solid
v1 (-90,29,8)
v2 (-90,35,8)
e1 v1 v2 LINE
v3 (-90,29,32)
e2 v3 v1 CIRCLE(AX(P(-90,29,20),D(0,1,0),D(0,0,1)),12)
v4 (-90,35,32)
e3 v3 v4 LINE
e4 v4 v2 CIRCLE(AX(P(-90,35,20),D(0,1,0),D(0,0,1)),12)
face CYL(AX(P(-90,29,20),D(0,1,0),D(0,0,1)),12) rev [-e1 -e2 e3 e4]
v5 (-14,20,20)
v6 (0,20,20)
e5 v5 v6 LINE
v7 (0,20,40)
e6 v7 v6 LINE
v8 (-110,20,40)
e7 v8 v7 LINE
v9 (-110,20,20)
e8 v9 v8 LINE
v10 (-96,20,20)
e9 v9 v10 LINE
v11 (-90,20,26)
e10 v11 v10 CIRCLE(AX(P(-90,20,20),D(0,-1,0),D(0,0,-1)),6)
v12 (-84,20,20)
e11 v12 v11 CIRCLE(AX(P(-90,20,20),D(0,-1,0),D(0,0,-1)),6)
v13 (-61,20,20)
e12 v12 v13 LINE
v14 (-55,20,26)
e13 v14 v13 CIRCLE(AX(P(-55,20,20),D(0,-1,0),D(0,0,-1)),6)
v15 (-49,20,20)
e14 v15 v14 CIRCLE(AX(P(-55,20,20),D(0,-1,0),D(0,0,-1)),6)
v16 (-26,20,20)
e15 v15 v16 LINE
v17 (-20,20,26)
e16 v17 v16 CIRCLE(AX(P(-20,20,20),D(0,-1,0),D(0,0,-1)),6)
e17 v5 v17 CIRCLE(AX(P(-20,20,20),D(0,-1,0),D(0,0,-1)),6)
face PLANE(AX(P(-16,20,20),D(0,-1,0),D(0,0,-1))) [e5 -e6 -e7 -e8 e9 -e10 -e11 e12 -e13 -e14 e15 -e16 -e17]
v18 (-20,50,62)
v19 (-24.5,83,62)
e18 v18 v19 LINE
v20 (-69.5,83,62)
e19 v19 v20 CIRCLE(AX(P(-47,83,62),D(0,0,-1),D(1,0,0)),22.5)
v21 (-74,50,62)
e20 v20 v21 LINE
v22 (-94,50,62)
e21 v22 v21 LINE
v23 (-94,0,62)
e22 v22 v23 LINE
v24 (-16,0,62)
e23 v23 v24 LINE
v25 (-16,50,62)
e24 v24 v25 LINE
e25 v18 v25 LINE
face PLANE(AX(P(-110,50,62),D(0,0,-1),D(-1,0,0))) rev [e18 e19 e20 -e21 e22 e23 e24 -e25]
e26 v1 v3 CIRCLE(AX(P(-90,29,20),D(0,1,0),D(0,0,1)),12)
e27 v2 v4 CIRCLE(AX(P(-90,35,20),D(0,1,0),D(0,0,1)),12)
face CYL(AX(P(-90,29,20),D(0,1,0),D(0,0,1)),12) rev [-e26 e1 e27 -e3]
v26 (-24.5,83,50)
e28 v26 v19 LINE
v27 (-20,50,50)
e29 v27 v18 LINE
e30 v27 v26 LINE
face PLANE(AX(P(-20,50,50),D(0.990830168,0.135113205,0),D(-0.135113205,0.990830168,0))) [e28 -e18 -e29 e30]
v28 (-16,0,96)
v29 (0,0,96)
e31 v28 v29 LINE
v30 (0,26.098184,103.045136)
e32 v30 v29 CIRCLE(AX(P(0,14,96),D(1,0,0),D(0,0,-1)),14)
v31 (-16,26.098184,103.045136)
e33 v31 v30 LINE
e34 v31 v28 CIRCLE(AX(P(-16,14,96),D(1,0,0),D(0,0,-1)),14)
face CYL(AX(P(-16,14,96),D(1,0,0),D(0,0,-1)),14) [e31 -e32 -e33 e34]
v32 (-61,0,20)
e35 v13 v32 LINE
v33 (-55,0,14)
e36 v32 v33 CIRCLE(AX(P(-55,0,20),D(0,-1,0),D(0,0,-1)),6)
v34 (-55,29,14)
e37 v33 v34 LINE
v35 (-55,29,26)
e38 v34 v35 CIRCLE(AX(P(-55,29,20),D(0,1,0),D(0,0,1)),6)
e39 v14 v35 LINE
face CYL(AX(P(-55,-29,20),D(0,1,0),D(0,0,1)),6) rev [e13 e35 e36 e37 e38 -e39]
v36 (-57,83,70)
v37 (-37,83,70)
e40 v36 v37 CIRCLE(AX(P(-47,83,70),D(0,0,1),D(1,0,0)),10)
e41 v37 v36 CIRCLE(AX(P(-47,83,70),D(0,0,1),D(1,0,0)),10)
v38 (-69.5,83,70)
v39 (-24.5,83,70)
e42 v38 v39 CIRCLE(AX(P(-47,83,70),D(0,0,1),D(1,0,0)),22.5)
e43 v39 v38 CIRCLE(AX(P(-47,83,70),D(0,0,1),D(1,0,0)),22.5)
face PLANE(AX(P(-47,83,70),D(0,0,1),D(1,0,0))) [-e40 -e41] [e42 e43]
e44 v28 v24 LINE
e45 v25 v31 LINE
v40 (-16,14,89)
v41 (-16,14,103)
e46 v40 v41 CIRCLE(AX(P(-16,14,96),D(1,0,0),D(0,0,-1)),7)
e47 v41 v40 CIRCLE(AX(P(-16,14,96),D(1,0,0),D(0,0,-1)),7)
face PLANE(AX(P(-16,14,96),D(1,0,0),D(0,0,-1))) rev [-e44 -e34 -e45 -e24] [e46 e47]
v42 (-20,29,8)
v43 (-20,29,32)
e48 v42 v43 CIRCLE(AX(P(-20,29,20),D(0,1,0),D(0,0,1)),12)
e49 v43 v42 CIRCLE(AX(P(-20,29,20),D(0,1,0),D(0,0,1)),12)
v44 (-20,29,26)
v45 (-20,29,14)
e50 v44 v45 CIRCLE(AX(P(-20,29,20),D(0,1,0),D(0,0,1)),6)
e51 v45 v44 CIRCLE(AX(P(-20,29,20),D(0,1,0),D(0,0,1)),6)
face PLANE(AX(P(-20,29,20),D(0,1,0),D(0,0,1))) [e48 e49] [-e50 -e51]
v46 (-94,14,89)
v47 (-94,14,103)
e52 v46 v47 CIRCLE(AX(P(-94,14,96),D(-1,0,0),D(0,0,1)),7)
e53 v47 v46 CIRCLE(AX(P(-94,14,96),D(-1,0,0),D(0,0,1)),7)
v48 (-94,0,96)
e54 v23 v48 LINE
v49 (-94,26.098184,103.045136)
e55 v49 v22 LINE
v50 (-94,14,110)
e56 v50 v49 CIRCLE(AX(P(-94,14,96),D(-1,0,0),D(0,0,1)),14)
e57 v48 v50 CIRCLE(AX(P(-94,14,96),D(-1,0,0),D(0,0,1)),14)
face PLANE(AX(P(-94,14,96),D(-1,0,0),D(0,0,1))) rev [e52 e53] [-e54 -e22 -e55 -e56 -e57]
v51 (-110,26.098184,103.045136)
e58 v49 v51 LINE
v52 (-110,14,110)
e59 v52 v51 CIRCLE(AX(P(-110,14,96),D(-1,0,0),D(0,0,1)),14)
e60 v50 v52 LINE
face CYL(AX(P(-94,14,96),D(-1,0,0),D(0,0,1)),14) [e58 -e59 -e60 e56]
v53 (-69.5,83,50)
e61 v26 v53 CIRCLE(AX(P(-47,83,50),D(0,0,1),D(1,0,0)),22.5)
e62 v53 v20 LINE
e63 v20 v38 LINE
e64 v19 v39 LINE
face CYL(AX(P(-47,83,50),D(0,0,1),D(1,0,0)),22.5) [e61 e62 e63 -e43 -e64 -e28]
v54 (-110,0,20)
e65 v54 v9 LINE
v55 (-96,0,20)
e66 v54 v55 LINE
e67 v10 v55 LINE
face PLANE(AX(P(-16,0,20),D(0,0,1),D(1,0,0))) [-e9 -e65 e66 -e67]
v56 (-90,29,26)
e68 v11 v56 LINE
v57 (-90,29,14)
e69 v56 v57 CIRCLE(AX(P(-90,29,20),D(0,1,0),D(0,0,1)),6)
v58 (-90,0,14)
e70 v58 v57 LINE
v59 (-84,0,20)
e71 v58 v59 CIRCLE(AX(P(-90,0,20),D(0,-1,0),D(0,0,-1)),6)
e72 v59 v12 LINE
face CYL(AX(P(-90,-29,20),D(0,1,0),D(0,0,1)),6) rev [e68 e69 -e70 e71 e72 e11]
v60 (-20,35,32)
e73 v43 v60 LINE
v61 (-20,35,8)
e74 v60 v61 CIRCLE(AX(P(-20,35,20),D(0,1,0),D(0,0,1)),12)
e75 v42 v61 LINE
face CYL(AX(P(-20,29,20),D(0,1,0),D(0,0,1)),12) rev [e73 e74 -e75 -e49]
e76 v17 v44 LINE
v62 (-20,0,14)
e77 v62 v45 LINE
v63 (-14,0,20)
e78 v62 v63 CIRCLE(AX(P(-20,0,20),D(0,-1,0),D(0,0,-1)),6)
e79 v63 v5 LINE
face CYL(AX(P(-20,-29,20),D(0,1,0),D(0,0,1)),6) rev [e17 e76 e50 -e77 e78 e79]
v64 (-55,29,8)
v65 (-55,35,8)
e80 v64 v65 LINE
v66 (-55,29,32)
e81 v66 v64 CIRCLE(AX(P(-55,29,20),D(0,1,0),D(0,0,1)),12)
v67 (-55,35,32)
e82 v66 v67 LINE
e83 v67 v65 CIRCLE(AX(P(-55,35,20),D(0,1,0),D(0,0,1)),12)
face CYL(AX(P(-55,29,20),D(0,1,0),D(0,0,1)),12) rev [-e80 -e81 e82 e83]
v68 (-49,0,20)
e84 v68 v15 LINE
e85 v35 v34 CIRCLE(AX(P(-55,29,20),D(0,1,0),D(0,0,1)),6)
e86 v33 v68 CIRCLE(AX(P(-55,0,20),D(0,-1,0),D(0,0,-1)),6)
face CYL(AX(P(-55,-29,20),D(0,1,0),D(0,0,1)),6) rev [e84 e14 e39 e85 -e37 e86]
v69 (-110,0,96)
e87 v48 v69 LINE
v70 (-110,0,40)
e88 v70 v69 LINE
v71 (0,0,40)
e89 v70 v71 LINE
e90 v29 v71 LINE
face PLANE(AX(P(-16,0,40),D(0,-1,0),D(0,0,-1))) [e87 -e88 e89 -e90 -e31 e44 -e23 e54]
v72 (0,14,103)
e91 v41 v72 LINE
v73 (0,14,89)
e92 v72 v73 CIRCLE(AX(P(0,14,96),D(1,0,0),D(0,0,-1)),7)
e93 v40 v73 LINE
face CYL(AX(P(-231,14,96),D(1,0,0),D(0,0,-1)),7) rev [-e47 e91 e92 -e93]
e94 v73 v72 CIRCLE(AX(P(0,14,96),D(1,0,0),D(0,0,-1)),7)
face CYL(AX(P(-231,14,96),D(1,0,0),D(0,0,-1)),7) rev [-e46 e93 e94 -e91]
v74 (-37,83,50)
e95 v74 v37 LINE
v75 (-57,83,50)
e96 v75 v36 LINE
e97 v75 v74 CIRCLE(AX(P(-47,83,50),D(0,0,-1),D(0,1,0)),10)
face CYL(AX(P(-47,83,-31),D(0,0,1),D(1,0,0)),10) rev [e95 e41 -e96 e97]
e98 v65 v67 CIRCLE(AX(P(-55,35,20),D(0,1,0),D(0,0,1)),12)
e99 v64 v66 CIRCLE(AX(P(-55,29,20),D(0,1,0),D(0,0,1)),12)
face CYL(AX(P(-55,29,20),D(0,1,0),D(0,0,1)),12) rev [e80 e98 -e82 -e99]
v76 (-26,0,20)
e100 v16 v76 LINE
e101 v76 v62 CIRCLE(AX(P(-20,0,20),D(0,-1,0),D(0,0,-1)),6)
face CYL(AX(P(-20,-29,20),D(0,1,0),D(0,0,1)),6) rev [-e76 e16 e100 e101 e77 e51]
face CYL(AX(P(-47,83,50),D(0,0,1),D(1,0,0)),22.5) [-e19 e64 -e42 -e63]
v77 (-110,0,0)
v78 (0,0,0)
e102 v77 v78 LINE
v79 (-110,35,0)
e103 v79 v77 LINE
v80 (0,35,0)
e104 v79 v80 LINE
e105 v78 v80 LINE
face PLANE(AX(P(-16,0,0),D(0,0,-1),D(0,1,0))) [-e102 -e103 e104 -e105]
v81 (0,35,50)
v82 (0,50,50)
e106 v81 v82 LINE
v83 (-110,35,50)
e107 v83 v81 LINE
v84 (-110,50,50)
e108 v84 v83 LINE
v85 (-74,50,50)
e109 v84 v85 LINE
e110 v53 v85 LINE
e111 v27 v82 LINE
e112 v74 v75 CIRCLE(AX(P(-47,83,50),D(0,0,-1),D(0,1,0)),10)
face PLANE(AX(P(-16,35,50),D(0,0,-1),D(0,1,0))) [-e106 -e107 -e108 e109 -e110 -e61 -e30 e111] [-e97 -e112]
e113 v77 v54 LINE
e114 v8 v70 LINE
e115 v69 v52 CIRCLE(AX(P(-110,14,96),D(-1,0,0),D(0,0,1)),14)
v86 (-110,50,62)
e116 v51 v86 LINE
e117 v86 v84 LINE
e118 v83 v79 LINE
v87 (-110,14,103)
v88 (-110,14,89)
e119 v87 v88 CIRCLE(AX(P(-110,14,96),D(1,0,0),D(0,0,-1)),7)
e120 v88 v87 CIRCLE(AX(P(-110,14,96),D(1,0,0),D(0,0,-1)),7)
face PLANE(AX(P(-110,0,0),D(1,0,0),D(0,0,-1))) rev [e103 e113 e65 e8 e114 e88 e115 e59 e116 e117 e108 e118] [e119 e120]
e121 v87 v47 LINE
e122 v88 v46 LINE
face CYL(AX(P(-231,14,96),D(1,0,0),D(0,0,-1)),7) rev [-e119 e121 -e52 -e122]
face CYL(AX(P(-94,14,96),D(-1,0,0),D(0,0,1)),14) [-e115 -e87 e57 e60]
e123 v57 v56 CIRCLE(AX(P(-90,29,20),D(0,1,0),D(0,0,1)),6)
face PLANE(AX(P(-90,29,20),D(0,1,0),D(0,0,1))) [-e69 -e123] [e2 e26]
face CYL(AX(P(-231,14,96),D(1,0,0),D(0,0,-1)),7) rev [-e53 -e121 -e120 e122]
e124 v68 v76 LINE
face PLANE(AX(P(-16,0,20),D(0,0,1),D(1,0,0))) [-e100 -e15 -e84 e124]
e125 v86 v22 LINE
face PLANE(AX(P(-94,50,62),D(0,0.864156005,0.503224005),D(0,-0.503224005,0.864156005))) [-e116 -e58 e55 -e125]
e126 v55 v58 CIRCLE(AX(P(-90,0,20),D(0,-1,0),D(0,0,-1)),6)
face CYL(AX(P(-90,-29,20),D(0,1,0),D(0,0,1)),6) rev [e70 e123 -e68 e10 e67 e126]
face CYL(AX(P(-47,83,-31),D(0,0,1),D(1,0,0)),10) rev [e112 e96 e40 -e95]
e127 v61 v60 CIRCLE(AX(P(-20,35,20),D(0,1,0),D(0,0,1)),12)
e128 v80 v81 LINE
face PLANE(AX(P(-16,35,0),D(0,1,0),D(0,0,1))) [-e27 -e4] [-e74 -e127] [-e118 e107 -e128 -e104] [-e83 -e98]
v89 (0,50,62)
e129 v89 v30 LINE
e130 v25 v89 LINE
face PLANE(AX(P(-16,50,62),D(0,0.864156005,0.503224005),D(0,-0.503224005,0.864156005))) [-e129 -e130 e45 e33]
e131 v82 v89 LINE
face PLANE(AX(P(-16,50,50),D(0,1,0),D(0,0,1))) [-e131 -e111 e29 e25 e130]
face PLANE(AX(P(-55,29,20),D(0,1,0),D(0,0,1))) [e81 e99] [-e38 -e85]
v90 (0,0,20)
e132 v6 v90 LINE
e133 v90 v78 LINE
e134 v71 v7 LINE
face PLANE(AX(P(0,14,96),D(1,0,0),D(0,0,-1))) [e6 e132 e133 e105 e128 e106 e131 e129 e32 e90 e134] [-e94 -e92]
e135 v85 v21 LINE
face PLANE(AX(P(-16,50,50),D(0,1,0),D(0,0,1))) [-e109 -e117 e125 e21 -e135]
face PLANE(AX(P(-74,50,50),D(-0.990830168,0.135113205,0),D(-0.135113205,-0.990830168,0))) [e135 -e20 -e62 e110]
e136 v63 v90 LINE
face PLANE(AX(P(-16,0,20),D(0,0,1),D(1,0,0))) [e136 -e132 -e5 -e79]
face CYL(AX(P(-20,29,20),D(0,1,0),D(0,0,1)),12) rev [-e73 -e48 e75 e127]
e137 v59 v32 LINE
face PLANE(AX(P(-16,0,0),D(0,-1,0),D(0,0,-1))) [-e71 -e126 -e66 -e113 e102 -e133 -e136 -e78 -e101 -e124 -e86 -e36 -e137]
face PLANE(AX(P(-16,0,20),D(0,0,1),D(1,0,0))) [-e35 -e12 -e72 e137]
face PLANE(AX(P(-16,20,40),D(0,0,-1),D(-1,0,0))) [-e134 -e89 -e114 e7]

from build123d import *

# Parameters (mm, degrees)
SIDE_ARM_16MM_DEPTH          = 16
BRACKET_BODY_94MM_DEPTH      = 94
SECOND_START                 = -16
SECOND_ARM_16MM_DEPTH        = 16
PIVOT_HOLE_SKETCH_14_R       = 7
PIVOT_HOLES_14_THROUGH_DEPTH = 231
BEARING_BOSS_45_DEPTH        = 8
BEARING_BOSS_45_DEPTH_BACK   = 12
BEARING_BOSS_SKETCH_45_R     = 22.5
BOSS_SUPPORT_WEB_12MM_DEPTH  = 12
BEARING_BORE_SKETCH_20_R     = 10
BEARING_BORE_20_DEPTH        = 101
COUNTERBORE_SKETCH_24_R      = 12
COUNTERBORES_24X6_DEPTH      = 6
MOUNTING_HOLE_SKETCH_12_R    = 6
MOUNTING_HOLES_12_DEPTH      = 58


with BuildPart() as part:
    # Side Arm Profile → Side Arm 16mm (new body)
    with BuildSketch(Plane(origin=(0, 0, 0), x_dir=(0, 0, -1), z_dir=(1, 0, 0))):
        with BuildLine():
            Line((0, 0), (-20, 0))
            Line((-20, 0), (-20, 20))
            Line((-20, 20), (-40, 20))
            Line((-40, 20), (-40, 0))
            Line((-40, 0), (-96, 0))
            ThreePointArc((-96, 0), (-109.516186166, 10.351341133), (-103.045136072, 26.098184068))
            Line((-103.045136072, 26.098184068), (-62, 50))
            Line((-62, 50), (-50, 50))
            Line((-50, 50), (-50, 35))
            Line((-50, 35), (0, 35))
            Line((0, 35), (0, 0))
        make_face()
    extrude(amount=-SIDE_ARM_16MM_DEPTH)

    # Bracket Body Profile → Bracket Body 94mm (add)
    with BuildSketch(Plane.ZY.offset(16)):
        Polygon((0, 0), (0, 35), (50, 35), (50, 50), (62, 50), (62, 0), (40, 0), (40, 20), (20, 20), (20, 0), align=None)
    extrude(amount=BRACKET_BODY_94MM_DEPTH)

    # Second Arm Profile → Second Arm 16mm (add)
    with BuildSketch(Plane.ZY.offset(110).offset(SECOND_START)):
        with BuildLine():
            Line((62, 0), (62, 50))
            Line((62, 50), (103.045136072, 26.098184068))
            ThreePointArc((103.045136072, 26.098184068), (109.516186166, 10.351341133), (96, 0))
            Line((96, 0), (62, 0))
        make_face()
    extrude(amount=SECOND_ARM_16MM_DEPTH)

    # Pivot Hole Sketch Ø14 → Pivot Holes Ø14 Through (cut)
    with BuildSketch(Plane(origin=(0, 0, 0), x_dir=(0, 0, -1), z_dir=(1, 0, 0))):
        with Locations((-96, 14)):
            Circle(PIVOT_HOLE_SKETCH_14_R)
    extrude(amount=-PIVOT_HOLES_14_THROUGH_DEPTH, mode=Mode.SUBTRACT)



with BuildPart() as body_2:
    # Bearing Boss Sketch Ø45 → Bearing Boss Ø45 (new, two sides: drawn at the far end of the back side and taken through both)
    with BuildSketch(Plane.XY.offset(62).offset(-BEARING_BOSS_45_DEPTH_BACK)):
        with Locations((-47, 83)):
            Circle(BEARING_BOSS_SKETCH_45_R)
    extrude(amount=BEARING_BOSS_45_DEPTH + BEARING_BOSS_45_DEPTH_BACK)


with BuildPart() as part_1:
    add(part.part)

    add(body_2.part)  # Boss Support Web 12mm merges body 2
    # Boss Support Web Profile → Boss Support Web 12mm (add)
    with BuildSketch(Plane.XY.offset(62)):
        with BuildLine():
            Line((-20, 50), (-24.5, 83))
            ThreePointArc((-24.5, 83), (-47, 60.5), (-69.5, 83))
            Line((-69.5, 83), (-74, 50))
            Line((-74, 50), (-20, 50))
        make_face()
    extrude(amount=-BOSS_SUPPORT_WEB_12MM_DEPTH)

    # Bearing Bore Sketch Ø20 → Bearing Bore Ø20 (cut)
    with BuildSketch(Plane.XY.offset(70)):
        with Locations((-47, 83)):
            Circle(BEARING_BORE_SKETCH_20_R)
    extrude(amount=-BEARING_BORE_20_DEPTH, mode=Mode.SUBTRACT)

    # Counterbore Sketch Ø24 → Counterbores Ø24x6 (cut)
    with BuildSketch(Plane(origin=(0, 35, 0), x_dir=(1, 0, 0), z_dir=(0, 1, 0))):
        with Locations(Location((-20, -20, 0), (0, 0, 270))):
            Circle(COUNTERBORE_SKETCH_24_R)
        with Locations(Location((-55, -20, 0), (0, 0, 270))):
            Circle(COUNTERBORE_SKETCH_24_R)
        with Locations(Location((-90, -20, 0), (0, 0, 270))):
            Circle(COUNTERBORE_SKETCH_24_R)
    extrude(amount=-COUNTERBORES_24X6_DEPTH, mode=Mode.SUBTRACT)

    # Mounting Hole Sketch Ø12 → Mounting Holes Ø12 (cut)
    with BuildSketch(Plane(origin=(0, 29, 0), x_dir=(1, 0, 0), z_dir=(0, 1, 0))):
        with Locations(Location((-20, -20, 0), (0, 0, 270))):
            Circle(MOUNTING_HOLE_SKETCH_12_R)
        with Locations(Location((-55, -20, 0), (0, 0, 270))):
            Circle(MOUNTING_HOLE_SKETCH_12_R)
        with Locations(Location((-90, -20, 0), (0, 0, 270))):
            Circle(MOUNTING_HOLE_SKETCH_12_R)
    extrude(amount=-MOUNTING_HOLES_12_DEPTH, mode=Mode.SUBTRACT)


solid = part_1.part
